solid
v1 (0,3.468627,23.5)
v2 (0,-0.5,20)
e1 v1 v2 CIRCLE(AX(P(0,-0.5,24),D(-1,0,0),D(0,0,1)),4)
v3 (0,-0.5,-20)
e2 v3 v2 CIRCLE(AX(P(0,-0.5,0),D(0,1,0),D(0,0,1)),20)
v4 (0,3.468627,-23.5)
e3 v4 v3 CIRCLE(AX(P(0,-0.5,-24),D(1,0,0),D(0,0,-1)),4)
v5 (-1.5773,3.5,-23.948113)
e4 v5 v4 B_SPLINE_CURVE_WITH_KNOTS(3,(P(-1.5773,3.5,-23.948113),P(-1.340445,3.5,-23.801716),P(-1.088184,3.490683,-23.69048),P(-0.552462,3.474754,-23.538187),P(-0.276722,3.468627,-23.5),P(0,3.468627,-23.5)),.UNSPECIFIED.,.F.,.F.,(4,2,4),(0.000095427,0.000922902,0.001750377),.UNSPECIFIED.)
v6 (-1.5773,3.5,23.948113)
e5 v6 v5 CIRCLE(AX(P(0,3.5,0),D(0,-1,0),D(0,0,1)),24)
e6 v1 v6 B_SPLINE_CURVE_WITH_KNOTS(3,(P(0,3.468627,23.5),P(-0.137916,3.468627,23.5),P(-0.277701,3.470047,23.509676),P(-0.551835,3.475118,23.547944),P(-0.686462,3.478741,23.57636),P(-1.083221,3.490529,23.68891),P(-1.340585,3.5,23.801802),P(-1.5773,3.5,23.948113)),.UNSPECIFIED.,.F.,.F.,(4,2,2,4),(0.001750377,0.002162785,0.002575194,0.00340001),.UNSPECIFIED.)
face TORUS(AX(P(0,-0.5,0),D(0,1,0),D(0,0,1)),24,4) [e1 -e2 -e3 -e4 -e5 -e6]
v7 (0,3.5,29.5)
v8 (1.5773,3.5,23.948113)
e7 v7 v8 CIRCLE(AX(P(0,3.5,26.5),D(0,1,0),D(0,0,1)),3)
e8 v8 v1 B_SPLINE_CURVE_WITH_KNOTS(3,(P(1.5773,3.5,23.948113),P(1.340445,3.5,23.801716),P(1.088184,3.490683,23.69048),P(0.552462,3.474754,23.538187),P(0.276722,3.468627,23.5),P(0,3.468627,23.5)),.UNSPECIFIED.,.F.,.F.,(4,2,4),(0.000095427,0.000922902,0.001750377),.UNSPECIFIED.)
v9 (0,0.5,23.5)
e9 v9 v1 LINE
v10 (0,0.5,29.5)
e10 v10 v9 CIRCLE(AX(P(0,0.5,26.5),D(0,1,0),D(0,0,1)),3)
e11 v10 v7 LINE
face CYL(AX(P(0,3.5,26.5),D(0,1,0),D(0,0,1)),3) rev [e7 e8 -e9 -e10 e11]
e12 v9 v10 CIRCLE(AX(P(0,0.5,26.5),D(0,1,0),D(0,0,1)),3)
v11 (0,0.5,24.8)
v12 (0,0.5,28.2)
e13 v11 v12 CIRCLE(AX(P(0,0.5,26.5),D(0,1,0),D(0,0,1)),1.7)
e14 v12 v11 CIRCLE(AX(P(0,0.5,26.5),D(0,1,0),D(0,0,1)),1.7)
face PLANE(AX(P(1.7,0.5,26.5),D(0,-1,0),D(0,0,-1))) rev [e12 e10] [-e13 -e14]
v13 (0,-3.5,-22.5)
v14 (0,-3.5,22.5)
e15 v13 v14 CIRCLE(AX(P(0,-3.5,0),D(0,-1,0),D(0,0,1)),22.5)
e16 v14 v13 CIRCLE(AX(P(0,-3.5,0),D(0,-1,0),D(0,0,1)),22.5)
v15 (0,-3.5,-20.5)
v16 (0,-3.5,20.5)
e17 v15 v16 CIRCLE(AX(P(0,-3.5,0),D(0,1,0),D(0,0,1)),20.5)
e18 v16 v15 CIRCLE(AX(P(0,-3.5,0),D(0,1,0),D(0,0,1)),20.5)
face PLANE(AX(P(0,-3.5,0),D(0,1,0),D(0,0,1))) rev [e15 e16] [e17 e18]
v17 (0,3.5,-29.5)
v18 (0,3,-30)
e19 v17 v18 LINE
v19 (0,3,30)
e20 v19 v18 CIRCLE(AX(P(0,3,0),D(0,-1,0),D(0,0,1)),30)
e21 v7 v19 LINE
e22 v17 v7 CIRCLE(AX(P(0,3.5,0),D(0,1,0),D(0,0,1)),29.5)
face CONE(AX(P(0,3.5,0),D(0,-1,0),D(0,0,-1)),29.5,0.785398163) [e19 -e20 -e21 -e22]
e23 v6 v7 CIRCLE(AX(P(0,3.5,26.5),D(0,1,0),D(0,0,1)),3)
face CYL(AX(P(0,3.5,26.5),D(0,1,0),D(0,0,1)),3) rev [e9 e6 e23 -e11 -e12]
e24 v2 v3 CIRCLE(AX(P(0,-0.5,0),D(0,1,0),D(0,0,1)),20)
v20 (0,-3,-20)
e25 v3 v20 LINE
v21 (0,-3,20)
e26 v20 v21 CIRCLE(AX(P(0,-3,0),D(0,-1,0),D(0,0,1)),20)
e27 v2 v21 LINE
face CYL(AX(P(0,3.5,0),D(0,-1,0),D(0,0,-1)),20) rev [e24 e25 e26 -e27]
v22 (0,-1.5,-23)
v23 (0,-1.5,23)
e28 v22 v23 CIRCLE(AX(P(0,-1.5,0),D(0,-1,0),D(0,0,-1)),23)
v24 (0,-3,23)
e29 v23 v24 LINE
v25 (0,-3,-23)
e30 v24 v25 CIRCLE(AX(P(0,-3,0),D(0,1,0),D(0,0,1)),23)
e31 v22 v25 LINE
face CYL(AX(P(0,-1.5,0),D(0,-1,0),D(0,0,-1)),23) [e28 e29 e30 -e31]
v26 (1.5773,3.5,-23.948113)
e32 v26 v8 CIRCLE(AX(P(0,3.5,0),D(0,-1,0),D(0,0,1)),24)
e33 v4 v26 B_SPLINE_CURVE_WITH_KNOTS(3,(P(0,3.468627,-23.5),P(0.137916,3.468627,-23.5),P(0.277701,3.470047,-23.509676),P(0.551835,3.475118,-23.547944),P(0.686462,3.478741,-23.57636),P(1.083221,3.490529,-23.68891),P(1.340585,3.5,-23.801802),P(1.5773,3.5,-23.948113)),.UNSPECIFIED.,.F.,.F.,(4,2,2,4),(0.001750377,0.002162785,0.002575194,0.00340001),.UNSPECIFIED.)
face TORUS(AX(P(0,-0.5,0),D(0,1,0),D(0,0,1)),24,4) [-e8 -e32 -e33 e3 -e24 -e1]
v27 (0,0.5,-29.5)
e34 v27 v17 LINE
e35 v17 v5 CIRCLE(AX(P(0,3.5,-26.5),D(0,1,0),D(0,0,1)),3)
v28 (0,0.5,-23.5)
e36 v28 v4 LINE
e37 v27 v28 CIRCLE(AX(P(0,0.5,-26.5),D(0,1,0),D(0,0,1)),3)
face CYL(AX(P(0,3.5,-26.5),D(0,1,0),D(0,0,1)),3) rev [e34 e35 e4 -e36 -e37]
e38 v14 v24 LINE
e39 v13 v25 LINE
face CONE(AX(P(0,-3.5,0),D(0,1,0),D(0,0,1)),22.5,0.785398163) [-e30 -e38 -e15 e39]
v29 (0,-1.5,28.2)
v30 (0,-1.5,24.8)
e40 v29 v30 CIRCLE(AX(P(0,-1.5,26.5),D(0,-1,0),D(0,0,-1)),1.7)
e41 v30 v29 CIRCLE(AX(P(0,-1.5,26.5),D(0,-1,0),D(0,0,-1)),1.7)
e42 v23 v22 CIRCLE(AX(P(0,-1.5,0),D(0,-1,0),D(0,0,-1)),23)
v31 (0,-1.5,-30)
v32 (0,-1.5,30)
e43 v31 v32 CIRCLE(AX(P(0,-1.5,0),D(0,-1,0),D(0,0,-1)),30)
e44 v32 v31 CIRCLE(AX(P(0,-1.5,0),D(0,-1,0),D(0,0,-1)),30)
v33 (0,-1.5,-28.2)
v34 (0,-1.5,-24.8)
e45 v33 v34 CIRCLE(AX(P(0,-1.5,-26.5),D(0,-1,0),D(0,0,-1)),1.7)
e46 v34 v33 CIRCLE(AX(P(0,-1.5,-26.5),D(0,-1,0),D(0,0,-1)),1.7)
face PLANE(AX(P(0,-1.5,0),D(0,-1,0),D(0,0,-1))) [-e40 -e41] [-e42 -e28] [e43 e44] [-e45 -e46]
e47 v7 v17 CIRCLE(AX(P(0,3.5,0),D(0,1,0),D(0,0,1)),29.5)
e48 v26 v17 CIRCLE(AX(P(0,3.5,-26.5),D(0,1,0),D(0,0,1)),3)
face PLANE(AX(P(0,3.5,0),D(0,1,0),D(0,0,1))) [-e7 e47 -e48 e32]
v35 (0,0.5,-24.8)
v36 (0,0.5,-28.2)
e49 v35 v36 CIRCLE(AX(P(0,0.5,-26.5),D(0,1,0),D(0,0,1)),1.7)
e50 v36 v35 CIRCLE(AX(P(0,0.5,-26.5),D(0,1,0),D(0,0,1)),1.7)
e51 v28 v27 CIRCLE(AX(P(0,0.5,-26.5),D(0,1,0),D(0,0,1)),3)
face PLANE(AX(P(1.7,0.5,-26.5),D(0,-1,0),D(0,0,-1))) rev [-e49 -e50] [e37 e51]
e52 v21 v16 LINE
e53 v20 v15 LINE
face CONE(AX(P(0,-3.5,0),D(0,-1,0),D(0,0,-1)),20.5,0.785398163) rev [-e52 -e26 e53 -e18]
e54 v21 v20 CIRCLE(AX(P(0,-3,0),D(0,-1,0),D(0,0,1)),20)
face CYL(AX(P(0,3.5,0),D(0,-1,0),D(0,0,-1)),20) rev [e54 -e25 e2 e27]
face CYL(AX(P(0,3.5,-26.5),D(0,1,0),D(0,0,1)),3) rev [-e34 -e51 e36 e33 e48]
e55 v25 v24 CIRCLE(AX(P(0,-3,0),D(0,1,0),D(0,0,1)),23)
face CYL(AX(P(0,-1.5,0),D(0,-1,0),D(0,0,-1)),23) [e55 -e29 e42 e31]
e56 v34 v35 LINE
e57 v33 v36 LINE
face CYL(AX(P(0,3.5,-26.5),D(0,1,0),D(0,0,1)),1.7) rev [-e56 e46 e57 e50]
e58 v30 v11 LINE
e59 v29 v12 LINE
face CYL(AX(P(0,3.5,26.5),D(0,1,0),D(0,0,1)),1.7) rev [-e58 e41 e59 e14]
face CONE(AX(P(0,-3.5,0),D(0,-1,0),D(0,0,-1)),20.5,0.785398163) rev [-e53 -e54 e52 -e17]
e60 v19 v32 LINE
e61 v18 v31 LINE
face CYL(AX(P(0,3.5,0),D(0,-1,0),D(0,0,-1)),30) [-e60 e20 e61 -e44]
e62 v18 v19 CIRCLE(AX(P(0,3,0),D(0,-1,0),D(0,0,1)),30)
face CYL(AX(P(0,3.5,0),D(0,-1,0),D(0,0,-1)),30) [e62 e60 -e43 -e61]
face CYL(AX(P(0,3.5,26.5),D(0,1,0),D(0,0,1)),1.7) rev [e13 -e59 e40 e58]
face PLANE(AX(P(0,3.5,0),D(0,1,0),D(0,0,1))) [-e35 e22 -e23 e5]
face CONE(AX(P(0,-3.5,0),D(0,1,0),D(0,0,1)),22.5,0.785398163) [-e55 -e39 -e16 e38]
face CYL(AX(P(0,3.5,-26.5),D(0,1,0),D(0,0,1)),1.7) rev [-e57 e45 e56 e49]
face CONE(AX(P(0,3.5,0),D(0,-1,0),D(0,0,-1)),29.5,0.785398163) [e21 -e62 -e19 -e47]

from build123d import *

# Parameters (mm, degrees)
SKETCH_1_R                = 30
SKETCH_1_R_2              = 20
EXTRUDE_1_DEPTH           = 3.5
SKETCH_2_OUTSIDE_W        = 79.028
SKETCH_2_OUTSIDE_H        = 79.028
SKETCH_2_OUTSIDE_R        = 23
CUT_EXTRUDE_1_DEPTH       = 2
FILLET_1_R                = 4
CHAMFER_1_SIZE            = 0.5
HOLE_WIZARD_1_D           = 3.4
HOLE_WIZARD_1_CBORE_D     = 6
HOLE_WIZARD_1_CBORE_DEPTH = 3


with BuildPart() as part:
    # 草图1 → 凸台-拉伸1 (new, symmetric)
    with BuildSketch(Plane(origin=(0, 0, 0), x_dir=(1, 0, 0), z_dir=(0, 1, 0))):
        with Locations(Location((0, 0, 0), (0, 0, 270))):
            Circle(SKETCH_1_R)
        with Locations(Location((0, 0, 0), (0, 0, 270))):
            Circle(SKETCH_1_R_2, mode=Mode.SUBTRACT)
    extrude(amount=EXTRUDE_1_DEPTH, both=True)

    # 草图2 outside → 切除-拉伸1 (cut)
    with BuildSketch(Plane.XZ.offset(3.5)):
        Rectangle(SKETCH_2_OUTSIDE_W, SKETCH_2_OUTSIDE_H)
        with Locations(Location((0, 0, 0), (0, 0, 270))):
            Circle(SKETCH_2_OUTSIDE_R, mode=Mode.SUBTRACT)
    extrude(amount=-CUT_EXTRUDE_1_DEPTH, mode=Mode.SUBTRACT)

    # 圆角1
    fillet_1_edges = [part.edges().sort_by_distance(p)[0] for p in [
        (0, 3.5, -20),
    ]]
    fillet(fillet_1_edges, radius=FILLET_1_R)

    # 倒角1
    chamfer_1_edges = [part.edges().sort_by_distance(p)[0] for p in [
        (0, -3.5, 23),
        (0, 3.5, -30),
        (0, -3.5, -20),
    ]]
    chamfer(chamfer_1_edges, length=CHAMFER_1_SIZE)

    # 打孔尺寸根据内六角圆柱头螺钉的类型1 (through all)
    with Locations(Plane(origin=(0, 3.5, 0), x_dir=(1, 0, 0), z_dir=(0, 1, 0))):
        with Locations((0, -26.5), (0, 26.5)):
            CounterBoreHole(HOLE_WIZARD_1_D / 2, HOLE_WIZARD_1_CBORE_D / 2, HOLE_WIZARD_1_CBORE_DEPTH)


solid = part.part
